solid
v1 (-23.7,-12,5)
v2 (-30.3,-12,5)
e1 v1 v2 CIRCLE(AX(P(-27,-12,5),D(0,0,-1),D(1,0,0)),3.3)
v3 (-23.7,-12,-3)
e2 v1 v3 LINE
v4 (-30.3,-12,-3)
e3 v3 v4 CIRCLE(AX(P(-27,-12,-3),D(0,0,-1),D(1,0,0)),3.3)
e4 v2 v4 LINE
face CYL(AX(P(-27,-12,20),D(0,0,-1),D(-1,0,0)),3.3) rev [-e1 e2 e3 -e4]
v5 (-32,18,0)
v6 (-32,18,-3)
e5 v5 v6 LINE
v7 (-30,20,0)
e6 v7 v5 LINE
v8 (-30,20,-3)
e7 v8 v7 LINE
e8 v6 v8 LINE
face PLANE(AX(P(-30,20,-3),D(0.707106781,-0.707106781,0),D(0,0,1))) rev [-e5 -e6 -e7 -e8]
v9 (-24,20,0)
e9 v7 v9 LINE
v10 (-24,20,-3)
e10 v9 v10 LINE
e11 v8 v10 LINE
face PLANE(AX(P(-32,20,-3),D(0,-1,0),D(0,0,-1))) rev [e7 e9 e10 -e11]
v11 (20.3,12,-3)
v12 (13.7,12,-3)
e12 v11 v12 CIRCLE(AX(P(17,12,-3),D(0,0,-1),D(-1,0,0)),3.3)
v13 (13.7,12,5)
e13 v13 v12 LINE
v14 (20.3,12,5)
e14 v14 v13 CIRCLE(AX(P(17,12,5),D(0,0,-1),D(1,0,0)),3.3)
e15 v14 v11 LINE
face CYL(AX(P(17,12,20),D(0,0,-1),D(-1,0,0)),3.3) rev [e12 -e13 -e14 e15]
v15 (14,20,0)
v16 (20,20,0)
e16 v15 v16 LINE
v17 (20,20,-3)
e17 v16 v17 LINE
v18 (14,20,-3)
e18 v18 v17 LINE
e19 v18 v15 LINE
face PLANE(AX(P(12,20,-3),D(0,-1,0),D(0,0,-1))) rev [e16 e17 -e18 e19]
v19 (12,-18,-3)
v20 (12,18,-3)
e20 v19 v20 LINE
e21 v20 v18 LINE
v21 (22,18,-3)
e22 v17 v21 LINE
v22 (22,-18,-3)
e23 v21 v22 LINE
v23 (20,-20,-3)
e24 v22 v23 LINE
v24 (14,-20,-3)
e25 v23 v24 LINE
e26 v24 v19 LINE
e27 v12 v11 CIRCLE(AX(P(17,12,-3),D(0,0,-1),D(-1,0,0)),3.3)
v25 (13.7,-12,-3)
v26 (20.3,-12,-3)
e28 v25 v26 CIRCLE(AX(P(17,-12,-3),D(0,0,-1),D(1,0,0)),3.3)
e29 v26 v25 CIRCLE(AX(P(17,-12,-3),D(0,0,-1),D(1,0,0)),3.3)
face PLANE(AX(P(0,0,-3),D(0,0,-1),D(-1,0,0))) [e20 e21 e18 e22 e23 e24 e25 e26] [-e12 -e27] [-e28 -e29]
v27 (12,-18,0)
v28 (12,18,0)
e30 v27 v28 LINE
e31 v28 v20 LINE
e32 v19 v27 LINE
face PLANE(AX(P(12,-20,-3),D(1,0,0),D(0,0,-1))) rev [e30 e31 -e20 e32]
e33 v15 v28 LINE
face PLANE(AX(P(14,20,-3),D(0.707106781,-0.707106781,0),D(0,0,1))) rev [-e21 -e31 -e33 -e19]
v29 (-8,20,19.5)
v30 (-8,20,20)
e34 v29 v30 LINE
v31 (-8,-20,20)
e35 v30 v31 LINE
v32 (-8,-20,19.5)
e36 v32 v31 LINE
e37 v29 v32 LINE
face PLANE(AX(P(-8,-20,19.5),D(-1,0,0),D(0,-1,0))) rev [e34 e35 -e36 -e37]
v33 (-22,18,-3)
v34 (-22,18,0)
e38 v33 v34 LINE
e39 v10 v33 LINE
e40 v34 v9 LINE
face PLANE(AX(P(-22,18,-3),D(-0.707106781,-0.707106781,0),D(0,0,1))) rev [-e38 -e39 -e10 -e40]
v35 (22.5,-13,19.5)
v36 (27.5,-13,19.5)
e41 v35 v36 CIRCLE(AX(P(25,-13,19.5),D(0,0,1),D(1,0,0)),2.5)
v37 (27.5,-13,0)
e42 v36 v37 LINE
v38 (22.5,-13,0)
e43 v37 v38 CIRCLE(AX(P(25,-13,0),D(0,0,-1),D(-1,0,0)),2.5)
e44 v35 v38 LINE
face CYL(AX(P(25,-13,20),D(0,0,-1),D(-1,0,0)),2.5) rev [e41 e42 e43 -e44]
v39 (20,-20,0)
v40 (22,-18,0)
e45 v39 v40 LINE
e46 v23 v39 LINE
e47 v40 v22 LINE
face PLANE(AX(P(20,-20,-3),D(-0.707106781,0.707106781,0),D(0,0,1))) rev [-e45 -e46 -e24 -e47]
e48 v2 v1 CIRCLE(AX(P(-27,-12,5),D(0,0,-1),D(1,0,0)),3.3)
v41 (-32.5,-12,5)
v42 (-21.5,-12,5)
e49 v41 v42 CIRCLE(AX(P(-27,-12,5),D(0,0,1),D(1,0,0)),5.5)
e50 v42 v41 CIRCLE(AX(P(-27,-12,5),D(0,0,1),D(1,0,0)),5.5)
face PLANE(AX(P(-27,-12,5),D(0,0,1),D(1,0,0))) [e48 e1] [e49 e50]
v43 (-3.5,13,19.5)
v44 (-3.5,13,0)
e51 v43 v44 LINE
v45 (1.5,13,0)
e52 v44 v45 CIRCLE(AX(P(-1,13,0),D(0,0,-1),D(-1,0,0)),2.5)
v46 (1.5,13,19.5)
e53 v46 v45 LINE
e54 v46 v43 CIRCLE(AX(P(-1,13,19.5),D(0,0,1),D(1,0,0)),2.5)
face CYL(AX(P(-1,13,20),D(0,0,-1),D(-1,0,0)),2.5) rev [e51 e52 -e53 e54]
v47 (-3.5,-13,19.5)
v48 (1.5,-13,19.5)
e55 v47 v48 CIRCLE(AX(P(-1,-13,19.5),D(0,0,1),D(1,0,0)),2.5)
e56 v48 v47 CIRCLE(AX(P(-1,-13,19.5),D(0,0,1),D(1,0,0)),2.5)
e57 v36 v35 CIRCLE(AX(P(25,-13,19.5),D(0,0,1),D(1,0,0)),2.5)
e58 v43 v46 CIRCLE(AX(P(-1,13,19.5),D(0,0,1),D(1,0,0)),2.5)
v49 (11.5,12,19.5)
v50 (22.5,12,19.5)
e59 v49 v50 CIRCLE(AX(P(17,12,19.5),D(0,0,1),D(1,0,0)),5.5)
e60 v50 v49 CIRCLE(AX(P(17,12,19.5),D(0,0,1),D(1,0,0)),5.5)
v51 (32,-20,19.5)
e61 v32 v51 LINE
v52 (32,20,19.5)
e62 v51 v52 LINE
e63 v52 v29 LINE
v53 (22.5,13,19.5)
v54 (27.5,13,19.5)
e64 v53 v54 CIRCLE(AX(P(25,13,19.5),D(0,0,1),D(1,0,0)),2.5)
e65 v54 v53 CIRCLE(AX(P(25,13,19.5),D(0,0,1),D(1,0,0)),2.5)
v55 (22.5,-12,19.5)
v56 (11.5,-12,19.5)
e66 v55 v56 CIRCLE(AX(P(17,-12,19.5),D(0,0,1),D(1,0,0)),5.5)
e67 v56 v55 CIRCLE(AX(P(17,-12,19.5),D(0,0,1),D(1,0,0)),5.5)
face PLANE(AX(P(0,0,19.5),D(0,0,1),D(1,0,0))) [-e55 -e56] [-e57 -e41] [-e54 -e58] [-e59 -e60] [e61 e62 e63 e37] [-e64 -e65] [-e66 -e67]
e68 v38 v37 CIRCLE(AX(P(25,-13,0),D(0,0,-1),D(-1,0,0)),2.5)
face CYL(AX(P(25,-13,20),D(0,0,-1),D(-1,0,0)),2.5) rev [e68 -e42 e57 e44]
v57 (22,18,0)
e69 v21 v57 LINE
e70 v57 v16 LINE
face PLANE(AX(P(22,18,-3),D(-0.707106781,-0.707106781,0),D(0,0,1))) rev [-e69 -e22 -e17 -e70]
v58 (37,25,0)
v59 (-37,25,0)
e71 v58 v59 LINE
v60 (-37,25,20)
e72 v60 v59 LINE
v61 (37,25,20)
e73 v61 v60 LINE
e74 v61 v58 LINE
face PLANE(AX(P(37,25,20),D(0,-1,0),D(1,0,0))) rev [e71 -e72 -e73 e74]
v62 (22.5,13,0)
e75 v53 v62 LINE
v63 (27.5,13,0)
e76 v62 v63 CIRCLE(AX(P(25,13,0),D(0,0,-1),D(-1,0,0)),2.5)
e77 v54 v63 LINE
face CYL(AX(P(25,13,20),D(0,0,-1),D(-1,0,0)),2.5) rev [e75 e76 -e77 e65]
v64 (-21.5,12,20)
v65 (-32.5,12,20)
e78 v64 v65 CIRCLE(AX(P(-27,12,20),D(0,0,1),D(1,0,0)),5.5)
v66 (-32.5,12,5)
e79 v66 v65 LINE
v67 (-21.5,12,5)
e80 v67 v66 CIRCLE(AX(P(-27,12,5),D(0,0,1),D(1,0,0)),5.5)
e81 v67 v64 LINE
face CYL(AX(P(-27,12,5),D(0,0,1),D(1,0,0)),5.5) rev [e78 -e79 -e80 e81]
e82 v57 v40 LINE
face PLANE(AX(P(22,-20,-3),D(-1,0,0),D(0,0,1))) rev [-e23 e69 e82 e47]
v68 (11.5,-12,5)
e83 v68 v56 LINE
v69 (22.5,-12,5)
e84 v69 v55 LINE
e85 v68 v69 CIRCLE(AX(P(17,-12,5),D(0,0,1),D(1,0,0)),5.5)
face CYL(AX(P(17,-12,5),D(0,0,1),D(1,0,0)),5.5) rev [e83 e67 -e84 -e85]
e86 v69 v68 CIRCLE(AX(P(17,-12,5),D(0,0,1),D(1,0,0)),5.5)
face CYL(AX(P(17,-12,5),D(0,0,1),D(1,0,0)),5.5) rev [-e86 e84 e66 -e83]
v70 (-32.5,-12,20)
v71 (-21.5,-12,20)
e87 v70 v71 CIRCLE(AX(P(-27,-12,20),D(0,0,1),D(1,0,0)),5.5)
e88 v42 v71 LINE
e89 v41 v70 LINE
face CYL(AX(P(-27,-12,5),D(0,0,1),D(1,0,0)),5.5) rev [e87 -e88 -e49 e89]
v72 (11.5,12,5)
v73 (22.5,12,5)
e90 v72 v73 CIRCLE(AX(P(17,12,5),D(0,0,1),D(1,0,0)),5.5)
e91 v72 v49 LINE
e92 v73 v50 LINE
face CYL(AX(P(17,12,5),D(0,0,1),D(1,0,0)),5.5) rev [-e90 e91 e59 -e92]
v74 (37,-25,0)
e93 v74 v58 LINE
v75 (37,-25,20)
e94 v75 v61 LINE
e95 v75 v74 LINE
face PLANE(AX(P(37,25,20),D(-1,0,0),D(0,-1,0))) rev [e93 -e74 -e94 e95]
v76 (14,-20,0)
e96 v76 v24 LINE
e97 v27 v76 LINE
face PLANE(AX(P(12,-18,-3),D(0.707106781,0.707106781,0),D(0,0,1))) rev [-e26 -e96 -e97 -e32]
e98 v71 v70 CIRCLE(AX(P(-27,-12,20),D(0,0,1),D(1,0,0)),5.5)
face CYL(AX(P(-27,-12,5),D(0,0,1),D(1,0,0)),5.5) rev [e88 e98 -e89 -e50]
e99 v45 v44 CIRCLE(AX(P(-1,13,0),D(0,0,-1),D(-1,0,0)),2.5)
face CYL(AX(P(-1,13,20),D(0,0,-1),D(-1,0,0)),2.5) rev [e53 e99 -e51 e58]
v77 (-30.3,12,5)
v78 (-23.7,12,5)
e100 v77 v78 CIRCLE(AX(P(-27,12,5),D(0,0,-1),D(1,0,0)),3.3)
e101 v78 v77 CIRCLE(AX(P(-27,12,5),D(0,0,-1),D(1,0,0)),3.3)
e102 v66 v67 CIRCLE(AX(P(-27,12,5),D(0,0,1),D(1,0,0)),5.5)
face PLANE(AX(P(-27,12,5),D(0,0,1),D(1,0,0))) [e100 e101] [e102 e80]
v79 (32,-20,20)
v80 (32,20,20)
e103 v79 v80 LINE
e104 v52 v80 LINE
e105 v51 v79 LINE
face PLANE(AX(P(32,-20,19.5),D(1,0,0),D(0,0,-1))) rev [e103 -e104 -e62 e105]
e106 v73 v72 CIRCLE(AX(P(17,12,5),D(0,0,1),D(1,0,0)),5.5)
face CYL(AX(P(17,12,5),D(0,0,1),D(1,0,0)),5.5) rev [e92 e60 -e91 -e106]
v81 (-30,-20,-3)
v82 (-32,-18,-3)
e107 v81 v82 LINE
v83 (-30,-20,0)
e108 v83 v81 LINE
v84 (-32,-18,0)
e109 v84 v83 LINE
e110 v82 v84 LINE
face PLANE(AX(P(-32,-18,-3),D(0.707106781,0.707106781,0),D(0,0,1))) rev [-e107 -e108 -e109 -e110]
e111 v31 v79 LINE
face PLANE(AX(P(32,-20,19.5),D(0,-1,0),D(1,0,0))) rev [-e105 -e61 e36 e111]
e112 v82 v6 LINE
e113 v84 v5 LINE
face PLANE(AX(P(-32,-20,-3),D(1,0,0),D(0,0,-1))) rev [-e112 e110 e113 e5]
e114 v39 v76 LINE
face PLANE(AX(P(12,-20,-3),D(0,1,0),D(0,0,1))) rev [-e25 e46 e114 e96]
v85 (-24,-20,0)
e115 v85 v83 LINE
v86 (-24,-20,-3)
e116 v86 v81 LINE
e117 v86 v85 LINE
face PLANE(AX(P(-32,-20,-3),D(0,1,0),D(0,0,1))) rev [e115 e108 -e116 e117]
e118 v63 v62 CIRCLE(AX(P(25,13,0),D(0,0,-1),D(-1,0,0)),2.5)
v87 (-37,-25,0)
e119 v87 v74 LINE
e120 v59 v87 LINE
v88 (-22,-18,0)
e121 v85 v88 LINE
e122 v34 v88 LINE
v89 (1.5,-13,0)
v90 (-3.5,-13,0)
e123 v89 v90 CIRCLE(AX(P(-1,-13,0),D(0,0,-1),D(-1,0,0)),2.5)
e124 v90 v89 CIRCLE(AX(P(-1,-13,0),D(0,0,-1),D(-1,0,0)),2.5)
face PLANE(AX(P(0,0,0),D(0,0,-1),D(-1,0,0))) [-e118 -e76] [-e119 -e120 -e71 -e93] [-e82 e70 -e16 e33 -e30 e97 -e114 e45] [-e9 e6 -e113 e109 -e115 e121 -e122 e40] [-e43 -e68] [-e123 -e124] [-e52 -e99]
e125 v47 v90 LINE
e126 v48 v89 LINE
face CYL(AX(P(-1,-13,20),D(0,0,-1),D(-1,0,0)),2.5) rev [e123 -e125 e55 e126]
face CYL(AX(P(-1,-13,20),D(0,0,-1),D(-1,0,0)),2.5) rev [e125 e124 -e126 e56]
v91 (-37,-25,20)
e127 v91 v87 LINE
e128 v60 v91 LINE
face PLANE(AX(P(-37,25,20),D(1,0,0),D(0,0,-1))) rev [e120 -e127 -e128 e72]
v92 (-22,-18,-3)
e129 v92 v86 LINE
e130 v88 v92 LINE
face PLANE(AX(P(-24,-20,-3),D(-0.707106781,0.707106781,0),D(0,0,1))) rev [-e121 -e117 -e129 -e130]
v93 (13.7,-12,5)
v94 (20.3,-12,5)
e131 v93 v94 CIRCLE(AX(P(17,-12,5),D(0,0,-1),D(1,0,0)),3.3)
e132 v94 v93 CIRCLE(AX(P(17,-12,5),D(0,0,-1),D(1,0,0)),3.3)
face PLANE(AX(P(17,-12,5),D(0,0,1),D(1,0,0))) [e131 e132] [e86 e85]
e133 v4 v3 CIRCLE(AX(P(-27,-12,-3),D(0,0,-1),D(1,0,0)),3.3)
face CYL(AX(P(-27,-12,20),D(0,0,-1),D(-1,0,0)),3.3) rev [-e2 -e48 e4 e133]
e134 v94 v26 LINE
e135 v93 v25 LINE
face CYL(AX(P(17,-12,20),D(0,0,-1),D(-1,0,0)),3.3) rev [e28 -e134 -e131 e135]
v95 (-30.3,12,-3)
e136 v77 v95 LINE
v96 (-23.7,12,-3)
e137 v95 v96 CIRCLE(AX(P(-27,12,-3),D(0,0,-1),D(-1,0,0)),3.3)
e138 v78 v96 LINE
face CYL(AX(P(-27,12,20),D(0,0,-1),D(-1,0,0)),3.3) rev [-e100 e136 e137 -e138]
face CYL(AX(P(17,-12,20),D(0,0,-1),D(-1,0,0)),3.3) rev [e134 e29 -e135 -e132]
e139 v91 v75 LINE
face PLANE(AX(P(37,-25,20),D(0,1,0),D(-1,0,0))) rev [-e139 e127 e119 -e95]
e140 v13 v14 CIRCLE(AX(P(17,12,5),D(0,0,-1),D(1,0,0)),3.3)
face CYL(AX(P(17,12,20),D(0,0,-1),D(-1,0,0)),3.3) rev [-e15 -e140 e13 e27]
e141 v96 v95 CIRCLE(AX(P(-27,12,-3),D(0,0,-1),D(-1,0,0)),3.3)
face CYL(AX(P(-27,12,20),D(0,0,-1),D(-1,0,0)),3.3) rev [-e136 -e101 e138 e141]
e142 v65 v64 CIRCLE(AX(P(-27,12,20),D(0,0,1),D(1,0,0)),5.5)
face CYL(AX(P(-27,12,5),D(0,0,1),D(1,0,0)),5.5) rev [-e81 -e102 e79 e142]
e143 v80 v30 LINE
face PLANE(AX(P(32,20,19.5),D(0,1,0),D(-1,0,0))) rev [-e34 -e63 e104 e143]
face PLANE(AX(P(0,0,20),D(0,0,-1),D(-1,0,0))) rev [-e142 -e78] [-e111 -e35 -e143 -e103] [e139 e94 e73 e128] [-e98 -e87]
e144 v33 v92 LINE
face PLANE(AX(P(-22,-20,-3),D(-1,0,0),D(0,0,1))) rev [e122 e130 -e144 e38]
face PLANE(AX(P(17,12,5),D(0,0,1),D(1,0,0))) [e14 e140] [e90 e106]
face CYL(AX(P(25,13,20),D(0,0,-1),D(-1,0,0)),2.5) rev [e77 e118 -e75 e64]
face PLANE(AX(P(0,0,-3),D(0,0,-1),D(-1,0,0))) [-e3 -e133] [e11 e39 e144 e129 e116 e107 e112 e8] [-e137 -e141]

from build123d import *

# Parameters (mm, degrees)
SKETCH1_W           = 74
SKETCH1_H           = 50
BOSS_EXTRUDE1_DEPTH = 20
SKETCH2_W           = 40
SKETCH2_H           = 40
CUT_EXTRUDE1_DEPTH  = 0.5
SKETCH3_W           = 10
SKETCH3_H           = 40
BOSS_EXTRUDE2_DEPTH = 3
CHAMFER1_SIZE       = 2
SKETCH4_R           = 3.3
SKETCH4_R_2         = 2.5
CUT_EXTRUDE2_DEPTH  = 51.229473419
SKETCH5_R           = 5.5
CUT_EXTRUDE3_DEPTH  = 15


with BuildPart() as part:
    # Sketch1 → Boss-Extrude1 (new body)
    with BuildSketch(Plane.XY):
        Rectangle(SKETCH1_W, SKETCH1_H)
    extrude(amount=BOSS_EXTRUDE1_DEPTH)

    # Sketch2 → Cut-Extrude1 (cut)
    with BuildSketch(Plane.XY.offset(20)):
        with Locations((12, 0)):
            Rectangle(SKETCH2_W, SKETCH2_H)
    extrude(amount=-CUT_EXTRUDE1_DEPTH, mode=Mode.SUBTRACT)

    # Sketch3 → Boss-Extrude2 (add)
    with BuildSketch(Plane(origin=(0, 0, 0), x_dir=(-1, 0, 0), z_dir=(0, 0, -1))):
        with Locations((-17, 0)):
            Rectangle(SKETCH3_W, SKETCH3_H)
        with Locations((27, 0)):
            Rectangle(SKETCH3_W, SKETCH3_H)
    extrude(amount=BOSS_EXTRUDE2_DEPTH)

    # Chamfer1
    chamfer1_edges = [part.edges().sort_by_distance(p)[0] for p in [
        (22, 20, -1.5),
        (22, -20, -1.5),
        (12, -20, -1.5),
        (12, 20, -1.5),
        (-22, 20, -1.5),
        (-22, -20, -1.5),
        (-32, -20, -1.5),
        (-32, 20, -1.5),
    ]]
    chamfer(chamfer1_edges, length=CHAMFER1_SIZE)

    # Sketch4 → Cut-Extrude2 (cut, through all)
    with BuildSketch(Plane(origin=(0, 0, -3), x_dir=(-1, 0, 0), z_dir=(0, 0, -1))):
        with Locations((-17, 12)):
            Circle(SKETCH4_R)
        with Locations((27, 12)):
            Circle(SKETCH4_R)
        with Locations((-25, 13)):
            Circle(SKETCH4_R_2)
        with Locations((1, 13)):
            Circle(SKETCH4_R_2)
        with Locations((1, -13)):
            Circle(SKETCH4_R_2)
        with Locations((-25, -13)):
            Circle(SKETCH4_R_2)
        with Locations(Location((27, -12, 0), (0, 0, 180))):
            Circle(SKETCH4_R)
        with Locations(Location((-17, -12, 0), (0, 0, 180))):
            Circle(SKETCH4_R)
    extrude(amount=-CUT_EXTRUDE2_DEPTH, mode=Mode.SUBTRACT)

    # Sketch5 → Cut-Extrude3 (cut)
    with BuildSketch(Plane.XY.offset(20)):
        with Locations((-27, 12)):
            Circle(SKETCH5_R)
        with Locations((-27, -12)):
            Circle(SKETCH5_R)
        with Locations((17, 12)):
            Circle(SKETCH5_R)
        with Locations((17, -12)):
            Circle(SKETCH5_R)
    extrude(amount=-CUT_EXTRUDE3_DEPTH, mode=Mode.SUBTRACT)


solid = part.part
